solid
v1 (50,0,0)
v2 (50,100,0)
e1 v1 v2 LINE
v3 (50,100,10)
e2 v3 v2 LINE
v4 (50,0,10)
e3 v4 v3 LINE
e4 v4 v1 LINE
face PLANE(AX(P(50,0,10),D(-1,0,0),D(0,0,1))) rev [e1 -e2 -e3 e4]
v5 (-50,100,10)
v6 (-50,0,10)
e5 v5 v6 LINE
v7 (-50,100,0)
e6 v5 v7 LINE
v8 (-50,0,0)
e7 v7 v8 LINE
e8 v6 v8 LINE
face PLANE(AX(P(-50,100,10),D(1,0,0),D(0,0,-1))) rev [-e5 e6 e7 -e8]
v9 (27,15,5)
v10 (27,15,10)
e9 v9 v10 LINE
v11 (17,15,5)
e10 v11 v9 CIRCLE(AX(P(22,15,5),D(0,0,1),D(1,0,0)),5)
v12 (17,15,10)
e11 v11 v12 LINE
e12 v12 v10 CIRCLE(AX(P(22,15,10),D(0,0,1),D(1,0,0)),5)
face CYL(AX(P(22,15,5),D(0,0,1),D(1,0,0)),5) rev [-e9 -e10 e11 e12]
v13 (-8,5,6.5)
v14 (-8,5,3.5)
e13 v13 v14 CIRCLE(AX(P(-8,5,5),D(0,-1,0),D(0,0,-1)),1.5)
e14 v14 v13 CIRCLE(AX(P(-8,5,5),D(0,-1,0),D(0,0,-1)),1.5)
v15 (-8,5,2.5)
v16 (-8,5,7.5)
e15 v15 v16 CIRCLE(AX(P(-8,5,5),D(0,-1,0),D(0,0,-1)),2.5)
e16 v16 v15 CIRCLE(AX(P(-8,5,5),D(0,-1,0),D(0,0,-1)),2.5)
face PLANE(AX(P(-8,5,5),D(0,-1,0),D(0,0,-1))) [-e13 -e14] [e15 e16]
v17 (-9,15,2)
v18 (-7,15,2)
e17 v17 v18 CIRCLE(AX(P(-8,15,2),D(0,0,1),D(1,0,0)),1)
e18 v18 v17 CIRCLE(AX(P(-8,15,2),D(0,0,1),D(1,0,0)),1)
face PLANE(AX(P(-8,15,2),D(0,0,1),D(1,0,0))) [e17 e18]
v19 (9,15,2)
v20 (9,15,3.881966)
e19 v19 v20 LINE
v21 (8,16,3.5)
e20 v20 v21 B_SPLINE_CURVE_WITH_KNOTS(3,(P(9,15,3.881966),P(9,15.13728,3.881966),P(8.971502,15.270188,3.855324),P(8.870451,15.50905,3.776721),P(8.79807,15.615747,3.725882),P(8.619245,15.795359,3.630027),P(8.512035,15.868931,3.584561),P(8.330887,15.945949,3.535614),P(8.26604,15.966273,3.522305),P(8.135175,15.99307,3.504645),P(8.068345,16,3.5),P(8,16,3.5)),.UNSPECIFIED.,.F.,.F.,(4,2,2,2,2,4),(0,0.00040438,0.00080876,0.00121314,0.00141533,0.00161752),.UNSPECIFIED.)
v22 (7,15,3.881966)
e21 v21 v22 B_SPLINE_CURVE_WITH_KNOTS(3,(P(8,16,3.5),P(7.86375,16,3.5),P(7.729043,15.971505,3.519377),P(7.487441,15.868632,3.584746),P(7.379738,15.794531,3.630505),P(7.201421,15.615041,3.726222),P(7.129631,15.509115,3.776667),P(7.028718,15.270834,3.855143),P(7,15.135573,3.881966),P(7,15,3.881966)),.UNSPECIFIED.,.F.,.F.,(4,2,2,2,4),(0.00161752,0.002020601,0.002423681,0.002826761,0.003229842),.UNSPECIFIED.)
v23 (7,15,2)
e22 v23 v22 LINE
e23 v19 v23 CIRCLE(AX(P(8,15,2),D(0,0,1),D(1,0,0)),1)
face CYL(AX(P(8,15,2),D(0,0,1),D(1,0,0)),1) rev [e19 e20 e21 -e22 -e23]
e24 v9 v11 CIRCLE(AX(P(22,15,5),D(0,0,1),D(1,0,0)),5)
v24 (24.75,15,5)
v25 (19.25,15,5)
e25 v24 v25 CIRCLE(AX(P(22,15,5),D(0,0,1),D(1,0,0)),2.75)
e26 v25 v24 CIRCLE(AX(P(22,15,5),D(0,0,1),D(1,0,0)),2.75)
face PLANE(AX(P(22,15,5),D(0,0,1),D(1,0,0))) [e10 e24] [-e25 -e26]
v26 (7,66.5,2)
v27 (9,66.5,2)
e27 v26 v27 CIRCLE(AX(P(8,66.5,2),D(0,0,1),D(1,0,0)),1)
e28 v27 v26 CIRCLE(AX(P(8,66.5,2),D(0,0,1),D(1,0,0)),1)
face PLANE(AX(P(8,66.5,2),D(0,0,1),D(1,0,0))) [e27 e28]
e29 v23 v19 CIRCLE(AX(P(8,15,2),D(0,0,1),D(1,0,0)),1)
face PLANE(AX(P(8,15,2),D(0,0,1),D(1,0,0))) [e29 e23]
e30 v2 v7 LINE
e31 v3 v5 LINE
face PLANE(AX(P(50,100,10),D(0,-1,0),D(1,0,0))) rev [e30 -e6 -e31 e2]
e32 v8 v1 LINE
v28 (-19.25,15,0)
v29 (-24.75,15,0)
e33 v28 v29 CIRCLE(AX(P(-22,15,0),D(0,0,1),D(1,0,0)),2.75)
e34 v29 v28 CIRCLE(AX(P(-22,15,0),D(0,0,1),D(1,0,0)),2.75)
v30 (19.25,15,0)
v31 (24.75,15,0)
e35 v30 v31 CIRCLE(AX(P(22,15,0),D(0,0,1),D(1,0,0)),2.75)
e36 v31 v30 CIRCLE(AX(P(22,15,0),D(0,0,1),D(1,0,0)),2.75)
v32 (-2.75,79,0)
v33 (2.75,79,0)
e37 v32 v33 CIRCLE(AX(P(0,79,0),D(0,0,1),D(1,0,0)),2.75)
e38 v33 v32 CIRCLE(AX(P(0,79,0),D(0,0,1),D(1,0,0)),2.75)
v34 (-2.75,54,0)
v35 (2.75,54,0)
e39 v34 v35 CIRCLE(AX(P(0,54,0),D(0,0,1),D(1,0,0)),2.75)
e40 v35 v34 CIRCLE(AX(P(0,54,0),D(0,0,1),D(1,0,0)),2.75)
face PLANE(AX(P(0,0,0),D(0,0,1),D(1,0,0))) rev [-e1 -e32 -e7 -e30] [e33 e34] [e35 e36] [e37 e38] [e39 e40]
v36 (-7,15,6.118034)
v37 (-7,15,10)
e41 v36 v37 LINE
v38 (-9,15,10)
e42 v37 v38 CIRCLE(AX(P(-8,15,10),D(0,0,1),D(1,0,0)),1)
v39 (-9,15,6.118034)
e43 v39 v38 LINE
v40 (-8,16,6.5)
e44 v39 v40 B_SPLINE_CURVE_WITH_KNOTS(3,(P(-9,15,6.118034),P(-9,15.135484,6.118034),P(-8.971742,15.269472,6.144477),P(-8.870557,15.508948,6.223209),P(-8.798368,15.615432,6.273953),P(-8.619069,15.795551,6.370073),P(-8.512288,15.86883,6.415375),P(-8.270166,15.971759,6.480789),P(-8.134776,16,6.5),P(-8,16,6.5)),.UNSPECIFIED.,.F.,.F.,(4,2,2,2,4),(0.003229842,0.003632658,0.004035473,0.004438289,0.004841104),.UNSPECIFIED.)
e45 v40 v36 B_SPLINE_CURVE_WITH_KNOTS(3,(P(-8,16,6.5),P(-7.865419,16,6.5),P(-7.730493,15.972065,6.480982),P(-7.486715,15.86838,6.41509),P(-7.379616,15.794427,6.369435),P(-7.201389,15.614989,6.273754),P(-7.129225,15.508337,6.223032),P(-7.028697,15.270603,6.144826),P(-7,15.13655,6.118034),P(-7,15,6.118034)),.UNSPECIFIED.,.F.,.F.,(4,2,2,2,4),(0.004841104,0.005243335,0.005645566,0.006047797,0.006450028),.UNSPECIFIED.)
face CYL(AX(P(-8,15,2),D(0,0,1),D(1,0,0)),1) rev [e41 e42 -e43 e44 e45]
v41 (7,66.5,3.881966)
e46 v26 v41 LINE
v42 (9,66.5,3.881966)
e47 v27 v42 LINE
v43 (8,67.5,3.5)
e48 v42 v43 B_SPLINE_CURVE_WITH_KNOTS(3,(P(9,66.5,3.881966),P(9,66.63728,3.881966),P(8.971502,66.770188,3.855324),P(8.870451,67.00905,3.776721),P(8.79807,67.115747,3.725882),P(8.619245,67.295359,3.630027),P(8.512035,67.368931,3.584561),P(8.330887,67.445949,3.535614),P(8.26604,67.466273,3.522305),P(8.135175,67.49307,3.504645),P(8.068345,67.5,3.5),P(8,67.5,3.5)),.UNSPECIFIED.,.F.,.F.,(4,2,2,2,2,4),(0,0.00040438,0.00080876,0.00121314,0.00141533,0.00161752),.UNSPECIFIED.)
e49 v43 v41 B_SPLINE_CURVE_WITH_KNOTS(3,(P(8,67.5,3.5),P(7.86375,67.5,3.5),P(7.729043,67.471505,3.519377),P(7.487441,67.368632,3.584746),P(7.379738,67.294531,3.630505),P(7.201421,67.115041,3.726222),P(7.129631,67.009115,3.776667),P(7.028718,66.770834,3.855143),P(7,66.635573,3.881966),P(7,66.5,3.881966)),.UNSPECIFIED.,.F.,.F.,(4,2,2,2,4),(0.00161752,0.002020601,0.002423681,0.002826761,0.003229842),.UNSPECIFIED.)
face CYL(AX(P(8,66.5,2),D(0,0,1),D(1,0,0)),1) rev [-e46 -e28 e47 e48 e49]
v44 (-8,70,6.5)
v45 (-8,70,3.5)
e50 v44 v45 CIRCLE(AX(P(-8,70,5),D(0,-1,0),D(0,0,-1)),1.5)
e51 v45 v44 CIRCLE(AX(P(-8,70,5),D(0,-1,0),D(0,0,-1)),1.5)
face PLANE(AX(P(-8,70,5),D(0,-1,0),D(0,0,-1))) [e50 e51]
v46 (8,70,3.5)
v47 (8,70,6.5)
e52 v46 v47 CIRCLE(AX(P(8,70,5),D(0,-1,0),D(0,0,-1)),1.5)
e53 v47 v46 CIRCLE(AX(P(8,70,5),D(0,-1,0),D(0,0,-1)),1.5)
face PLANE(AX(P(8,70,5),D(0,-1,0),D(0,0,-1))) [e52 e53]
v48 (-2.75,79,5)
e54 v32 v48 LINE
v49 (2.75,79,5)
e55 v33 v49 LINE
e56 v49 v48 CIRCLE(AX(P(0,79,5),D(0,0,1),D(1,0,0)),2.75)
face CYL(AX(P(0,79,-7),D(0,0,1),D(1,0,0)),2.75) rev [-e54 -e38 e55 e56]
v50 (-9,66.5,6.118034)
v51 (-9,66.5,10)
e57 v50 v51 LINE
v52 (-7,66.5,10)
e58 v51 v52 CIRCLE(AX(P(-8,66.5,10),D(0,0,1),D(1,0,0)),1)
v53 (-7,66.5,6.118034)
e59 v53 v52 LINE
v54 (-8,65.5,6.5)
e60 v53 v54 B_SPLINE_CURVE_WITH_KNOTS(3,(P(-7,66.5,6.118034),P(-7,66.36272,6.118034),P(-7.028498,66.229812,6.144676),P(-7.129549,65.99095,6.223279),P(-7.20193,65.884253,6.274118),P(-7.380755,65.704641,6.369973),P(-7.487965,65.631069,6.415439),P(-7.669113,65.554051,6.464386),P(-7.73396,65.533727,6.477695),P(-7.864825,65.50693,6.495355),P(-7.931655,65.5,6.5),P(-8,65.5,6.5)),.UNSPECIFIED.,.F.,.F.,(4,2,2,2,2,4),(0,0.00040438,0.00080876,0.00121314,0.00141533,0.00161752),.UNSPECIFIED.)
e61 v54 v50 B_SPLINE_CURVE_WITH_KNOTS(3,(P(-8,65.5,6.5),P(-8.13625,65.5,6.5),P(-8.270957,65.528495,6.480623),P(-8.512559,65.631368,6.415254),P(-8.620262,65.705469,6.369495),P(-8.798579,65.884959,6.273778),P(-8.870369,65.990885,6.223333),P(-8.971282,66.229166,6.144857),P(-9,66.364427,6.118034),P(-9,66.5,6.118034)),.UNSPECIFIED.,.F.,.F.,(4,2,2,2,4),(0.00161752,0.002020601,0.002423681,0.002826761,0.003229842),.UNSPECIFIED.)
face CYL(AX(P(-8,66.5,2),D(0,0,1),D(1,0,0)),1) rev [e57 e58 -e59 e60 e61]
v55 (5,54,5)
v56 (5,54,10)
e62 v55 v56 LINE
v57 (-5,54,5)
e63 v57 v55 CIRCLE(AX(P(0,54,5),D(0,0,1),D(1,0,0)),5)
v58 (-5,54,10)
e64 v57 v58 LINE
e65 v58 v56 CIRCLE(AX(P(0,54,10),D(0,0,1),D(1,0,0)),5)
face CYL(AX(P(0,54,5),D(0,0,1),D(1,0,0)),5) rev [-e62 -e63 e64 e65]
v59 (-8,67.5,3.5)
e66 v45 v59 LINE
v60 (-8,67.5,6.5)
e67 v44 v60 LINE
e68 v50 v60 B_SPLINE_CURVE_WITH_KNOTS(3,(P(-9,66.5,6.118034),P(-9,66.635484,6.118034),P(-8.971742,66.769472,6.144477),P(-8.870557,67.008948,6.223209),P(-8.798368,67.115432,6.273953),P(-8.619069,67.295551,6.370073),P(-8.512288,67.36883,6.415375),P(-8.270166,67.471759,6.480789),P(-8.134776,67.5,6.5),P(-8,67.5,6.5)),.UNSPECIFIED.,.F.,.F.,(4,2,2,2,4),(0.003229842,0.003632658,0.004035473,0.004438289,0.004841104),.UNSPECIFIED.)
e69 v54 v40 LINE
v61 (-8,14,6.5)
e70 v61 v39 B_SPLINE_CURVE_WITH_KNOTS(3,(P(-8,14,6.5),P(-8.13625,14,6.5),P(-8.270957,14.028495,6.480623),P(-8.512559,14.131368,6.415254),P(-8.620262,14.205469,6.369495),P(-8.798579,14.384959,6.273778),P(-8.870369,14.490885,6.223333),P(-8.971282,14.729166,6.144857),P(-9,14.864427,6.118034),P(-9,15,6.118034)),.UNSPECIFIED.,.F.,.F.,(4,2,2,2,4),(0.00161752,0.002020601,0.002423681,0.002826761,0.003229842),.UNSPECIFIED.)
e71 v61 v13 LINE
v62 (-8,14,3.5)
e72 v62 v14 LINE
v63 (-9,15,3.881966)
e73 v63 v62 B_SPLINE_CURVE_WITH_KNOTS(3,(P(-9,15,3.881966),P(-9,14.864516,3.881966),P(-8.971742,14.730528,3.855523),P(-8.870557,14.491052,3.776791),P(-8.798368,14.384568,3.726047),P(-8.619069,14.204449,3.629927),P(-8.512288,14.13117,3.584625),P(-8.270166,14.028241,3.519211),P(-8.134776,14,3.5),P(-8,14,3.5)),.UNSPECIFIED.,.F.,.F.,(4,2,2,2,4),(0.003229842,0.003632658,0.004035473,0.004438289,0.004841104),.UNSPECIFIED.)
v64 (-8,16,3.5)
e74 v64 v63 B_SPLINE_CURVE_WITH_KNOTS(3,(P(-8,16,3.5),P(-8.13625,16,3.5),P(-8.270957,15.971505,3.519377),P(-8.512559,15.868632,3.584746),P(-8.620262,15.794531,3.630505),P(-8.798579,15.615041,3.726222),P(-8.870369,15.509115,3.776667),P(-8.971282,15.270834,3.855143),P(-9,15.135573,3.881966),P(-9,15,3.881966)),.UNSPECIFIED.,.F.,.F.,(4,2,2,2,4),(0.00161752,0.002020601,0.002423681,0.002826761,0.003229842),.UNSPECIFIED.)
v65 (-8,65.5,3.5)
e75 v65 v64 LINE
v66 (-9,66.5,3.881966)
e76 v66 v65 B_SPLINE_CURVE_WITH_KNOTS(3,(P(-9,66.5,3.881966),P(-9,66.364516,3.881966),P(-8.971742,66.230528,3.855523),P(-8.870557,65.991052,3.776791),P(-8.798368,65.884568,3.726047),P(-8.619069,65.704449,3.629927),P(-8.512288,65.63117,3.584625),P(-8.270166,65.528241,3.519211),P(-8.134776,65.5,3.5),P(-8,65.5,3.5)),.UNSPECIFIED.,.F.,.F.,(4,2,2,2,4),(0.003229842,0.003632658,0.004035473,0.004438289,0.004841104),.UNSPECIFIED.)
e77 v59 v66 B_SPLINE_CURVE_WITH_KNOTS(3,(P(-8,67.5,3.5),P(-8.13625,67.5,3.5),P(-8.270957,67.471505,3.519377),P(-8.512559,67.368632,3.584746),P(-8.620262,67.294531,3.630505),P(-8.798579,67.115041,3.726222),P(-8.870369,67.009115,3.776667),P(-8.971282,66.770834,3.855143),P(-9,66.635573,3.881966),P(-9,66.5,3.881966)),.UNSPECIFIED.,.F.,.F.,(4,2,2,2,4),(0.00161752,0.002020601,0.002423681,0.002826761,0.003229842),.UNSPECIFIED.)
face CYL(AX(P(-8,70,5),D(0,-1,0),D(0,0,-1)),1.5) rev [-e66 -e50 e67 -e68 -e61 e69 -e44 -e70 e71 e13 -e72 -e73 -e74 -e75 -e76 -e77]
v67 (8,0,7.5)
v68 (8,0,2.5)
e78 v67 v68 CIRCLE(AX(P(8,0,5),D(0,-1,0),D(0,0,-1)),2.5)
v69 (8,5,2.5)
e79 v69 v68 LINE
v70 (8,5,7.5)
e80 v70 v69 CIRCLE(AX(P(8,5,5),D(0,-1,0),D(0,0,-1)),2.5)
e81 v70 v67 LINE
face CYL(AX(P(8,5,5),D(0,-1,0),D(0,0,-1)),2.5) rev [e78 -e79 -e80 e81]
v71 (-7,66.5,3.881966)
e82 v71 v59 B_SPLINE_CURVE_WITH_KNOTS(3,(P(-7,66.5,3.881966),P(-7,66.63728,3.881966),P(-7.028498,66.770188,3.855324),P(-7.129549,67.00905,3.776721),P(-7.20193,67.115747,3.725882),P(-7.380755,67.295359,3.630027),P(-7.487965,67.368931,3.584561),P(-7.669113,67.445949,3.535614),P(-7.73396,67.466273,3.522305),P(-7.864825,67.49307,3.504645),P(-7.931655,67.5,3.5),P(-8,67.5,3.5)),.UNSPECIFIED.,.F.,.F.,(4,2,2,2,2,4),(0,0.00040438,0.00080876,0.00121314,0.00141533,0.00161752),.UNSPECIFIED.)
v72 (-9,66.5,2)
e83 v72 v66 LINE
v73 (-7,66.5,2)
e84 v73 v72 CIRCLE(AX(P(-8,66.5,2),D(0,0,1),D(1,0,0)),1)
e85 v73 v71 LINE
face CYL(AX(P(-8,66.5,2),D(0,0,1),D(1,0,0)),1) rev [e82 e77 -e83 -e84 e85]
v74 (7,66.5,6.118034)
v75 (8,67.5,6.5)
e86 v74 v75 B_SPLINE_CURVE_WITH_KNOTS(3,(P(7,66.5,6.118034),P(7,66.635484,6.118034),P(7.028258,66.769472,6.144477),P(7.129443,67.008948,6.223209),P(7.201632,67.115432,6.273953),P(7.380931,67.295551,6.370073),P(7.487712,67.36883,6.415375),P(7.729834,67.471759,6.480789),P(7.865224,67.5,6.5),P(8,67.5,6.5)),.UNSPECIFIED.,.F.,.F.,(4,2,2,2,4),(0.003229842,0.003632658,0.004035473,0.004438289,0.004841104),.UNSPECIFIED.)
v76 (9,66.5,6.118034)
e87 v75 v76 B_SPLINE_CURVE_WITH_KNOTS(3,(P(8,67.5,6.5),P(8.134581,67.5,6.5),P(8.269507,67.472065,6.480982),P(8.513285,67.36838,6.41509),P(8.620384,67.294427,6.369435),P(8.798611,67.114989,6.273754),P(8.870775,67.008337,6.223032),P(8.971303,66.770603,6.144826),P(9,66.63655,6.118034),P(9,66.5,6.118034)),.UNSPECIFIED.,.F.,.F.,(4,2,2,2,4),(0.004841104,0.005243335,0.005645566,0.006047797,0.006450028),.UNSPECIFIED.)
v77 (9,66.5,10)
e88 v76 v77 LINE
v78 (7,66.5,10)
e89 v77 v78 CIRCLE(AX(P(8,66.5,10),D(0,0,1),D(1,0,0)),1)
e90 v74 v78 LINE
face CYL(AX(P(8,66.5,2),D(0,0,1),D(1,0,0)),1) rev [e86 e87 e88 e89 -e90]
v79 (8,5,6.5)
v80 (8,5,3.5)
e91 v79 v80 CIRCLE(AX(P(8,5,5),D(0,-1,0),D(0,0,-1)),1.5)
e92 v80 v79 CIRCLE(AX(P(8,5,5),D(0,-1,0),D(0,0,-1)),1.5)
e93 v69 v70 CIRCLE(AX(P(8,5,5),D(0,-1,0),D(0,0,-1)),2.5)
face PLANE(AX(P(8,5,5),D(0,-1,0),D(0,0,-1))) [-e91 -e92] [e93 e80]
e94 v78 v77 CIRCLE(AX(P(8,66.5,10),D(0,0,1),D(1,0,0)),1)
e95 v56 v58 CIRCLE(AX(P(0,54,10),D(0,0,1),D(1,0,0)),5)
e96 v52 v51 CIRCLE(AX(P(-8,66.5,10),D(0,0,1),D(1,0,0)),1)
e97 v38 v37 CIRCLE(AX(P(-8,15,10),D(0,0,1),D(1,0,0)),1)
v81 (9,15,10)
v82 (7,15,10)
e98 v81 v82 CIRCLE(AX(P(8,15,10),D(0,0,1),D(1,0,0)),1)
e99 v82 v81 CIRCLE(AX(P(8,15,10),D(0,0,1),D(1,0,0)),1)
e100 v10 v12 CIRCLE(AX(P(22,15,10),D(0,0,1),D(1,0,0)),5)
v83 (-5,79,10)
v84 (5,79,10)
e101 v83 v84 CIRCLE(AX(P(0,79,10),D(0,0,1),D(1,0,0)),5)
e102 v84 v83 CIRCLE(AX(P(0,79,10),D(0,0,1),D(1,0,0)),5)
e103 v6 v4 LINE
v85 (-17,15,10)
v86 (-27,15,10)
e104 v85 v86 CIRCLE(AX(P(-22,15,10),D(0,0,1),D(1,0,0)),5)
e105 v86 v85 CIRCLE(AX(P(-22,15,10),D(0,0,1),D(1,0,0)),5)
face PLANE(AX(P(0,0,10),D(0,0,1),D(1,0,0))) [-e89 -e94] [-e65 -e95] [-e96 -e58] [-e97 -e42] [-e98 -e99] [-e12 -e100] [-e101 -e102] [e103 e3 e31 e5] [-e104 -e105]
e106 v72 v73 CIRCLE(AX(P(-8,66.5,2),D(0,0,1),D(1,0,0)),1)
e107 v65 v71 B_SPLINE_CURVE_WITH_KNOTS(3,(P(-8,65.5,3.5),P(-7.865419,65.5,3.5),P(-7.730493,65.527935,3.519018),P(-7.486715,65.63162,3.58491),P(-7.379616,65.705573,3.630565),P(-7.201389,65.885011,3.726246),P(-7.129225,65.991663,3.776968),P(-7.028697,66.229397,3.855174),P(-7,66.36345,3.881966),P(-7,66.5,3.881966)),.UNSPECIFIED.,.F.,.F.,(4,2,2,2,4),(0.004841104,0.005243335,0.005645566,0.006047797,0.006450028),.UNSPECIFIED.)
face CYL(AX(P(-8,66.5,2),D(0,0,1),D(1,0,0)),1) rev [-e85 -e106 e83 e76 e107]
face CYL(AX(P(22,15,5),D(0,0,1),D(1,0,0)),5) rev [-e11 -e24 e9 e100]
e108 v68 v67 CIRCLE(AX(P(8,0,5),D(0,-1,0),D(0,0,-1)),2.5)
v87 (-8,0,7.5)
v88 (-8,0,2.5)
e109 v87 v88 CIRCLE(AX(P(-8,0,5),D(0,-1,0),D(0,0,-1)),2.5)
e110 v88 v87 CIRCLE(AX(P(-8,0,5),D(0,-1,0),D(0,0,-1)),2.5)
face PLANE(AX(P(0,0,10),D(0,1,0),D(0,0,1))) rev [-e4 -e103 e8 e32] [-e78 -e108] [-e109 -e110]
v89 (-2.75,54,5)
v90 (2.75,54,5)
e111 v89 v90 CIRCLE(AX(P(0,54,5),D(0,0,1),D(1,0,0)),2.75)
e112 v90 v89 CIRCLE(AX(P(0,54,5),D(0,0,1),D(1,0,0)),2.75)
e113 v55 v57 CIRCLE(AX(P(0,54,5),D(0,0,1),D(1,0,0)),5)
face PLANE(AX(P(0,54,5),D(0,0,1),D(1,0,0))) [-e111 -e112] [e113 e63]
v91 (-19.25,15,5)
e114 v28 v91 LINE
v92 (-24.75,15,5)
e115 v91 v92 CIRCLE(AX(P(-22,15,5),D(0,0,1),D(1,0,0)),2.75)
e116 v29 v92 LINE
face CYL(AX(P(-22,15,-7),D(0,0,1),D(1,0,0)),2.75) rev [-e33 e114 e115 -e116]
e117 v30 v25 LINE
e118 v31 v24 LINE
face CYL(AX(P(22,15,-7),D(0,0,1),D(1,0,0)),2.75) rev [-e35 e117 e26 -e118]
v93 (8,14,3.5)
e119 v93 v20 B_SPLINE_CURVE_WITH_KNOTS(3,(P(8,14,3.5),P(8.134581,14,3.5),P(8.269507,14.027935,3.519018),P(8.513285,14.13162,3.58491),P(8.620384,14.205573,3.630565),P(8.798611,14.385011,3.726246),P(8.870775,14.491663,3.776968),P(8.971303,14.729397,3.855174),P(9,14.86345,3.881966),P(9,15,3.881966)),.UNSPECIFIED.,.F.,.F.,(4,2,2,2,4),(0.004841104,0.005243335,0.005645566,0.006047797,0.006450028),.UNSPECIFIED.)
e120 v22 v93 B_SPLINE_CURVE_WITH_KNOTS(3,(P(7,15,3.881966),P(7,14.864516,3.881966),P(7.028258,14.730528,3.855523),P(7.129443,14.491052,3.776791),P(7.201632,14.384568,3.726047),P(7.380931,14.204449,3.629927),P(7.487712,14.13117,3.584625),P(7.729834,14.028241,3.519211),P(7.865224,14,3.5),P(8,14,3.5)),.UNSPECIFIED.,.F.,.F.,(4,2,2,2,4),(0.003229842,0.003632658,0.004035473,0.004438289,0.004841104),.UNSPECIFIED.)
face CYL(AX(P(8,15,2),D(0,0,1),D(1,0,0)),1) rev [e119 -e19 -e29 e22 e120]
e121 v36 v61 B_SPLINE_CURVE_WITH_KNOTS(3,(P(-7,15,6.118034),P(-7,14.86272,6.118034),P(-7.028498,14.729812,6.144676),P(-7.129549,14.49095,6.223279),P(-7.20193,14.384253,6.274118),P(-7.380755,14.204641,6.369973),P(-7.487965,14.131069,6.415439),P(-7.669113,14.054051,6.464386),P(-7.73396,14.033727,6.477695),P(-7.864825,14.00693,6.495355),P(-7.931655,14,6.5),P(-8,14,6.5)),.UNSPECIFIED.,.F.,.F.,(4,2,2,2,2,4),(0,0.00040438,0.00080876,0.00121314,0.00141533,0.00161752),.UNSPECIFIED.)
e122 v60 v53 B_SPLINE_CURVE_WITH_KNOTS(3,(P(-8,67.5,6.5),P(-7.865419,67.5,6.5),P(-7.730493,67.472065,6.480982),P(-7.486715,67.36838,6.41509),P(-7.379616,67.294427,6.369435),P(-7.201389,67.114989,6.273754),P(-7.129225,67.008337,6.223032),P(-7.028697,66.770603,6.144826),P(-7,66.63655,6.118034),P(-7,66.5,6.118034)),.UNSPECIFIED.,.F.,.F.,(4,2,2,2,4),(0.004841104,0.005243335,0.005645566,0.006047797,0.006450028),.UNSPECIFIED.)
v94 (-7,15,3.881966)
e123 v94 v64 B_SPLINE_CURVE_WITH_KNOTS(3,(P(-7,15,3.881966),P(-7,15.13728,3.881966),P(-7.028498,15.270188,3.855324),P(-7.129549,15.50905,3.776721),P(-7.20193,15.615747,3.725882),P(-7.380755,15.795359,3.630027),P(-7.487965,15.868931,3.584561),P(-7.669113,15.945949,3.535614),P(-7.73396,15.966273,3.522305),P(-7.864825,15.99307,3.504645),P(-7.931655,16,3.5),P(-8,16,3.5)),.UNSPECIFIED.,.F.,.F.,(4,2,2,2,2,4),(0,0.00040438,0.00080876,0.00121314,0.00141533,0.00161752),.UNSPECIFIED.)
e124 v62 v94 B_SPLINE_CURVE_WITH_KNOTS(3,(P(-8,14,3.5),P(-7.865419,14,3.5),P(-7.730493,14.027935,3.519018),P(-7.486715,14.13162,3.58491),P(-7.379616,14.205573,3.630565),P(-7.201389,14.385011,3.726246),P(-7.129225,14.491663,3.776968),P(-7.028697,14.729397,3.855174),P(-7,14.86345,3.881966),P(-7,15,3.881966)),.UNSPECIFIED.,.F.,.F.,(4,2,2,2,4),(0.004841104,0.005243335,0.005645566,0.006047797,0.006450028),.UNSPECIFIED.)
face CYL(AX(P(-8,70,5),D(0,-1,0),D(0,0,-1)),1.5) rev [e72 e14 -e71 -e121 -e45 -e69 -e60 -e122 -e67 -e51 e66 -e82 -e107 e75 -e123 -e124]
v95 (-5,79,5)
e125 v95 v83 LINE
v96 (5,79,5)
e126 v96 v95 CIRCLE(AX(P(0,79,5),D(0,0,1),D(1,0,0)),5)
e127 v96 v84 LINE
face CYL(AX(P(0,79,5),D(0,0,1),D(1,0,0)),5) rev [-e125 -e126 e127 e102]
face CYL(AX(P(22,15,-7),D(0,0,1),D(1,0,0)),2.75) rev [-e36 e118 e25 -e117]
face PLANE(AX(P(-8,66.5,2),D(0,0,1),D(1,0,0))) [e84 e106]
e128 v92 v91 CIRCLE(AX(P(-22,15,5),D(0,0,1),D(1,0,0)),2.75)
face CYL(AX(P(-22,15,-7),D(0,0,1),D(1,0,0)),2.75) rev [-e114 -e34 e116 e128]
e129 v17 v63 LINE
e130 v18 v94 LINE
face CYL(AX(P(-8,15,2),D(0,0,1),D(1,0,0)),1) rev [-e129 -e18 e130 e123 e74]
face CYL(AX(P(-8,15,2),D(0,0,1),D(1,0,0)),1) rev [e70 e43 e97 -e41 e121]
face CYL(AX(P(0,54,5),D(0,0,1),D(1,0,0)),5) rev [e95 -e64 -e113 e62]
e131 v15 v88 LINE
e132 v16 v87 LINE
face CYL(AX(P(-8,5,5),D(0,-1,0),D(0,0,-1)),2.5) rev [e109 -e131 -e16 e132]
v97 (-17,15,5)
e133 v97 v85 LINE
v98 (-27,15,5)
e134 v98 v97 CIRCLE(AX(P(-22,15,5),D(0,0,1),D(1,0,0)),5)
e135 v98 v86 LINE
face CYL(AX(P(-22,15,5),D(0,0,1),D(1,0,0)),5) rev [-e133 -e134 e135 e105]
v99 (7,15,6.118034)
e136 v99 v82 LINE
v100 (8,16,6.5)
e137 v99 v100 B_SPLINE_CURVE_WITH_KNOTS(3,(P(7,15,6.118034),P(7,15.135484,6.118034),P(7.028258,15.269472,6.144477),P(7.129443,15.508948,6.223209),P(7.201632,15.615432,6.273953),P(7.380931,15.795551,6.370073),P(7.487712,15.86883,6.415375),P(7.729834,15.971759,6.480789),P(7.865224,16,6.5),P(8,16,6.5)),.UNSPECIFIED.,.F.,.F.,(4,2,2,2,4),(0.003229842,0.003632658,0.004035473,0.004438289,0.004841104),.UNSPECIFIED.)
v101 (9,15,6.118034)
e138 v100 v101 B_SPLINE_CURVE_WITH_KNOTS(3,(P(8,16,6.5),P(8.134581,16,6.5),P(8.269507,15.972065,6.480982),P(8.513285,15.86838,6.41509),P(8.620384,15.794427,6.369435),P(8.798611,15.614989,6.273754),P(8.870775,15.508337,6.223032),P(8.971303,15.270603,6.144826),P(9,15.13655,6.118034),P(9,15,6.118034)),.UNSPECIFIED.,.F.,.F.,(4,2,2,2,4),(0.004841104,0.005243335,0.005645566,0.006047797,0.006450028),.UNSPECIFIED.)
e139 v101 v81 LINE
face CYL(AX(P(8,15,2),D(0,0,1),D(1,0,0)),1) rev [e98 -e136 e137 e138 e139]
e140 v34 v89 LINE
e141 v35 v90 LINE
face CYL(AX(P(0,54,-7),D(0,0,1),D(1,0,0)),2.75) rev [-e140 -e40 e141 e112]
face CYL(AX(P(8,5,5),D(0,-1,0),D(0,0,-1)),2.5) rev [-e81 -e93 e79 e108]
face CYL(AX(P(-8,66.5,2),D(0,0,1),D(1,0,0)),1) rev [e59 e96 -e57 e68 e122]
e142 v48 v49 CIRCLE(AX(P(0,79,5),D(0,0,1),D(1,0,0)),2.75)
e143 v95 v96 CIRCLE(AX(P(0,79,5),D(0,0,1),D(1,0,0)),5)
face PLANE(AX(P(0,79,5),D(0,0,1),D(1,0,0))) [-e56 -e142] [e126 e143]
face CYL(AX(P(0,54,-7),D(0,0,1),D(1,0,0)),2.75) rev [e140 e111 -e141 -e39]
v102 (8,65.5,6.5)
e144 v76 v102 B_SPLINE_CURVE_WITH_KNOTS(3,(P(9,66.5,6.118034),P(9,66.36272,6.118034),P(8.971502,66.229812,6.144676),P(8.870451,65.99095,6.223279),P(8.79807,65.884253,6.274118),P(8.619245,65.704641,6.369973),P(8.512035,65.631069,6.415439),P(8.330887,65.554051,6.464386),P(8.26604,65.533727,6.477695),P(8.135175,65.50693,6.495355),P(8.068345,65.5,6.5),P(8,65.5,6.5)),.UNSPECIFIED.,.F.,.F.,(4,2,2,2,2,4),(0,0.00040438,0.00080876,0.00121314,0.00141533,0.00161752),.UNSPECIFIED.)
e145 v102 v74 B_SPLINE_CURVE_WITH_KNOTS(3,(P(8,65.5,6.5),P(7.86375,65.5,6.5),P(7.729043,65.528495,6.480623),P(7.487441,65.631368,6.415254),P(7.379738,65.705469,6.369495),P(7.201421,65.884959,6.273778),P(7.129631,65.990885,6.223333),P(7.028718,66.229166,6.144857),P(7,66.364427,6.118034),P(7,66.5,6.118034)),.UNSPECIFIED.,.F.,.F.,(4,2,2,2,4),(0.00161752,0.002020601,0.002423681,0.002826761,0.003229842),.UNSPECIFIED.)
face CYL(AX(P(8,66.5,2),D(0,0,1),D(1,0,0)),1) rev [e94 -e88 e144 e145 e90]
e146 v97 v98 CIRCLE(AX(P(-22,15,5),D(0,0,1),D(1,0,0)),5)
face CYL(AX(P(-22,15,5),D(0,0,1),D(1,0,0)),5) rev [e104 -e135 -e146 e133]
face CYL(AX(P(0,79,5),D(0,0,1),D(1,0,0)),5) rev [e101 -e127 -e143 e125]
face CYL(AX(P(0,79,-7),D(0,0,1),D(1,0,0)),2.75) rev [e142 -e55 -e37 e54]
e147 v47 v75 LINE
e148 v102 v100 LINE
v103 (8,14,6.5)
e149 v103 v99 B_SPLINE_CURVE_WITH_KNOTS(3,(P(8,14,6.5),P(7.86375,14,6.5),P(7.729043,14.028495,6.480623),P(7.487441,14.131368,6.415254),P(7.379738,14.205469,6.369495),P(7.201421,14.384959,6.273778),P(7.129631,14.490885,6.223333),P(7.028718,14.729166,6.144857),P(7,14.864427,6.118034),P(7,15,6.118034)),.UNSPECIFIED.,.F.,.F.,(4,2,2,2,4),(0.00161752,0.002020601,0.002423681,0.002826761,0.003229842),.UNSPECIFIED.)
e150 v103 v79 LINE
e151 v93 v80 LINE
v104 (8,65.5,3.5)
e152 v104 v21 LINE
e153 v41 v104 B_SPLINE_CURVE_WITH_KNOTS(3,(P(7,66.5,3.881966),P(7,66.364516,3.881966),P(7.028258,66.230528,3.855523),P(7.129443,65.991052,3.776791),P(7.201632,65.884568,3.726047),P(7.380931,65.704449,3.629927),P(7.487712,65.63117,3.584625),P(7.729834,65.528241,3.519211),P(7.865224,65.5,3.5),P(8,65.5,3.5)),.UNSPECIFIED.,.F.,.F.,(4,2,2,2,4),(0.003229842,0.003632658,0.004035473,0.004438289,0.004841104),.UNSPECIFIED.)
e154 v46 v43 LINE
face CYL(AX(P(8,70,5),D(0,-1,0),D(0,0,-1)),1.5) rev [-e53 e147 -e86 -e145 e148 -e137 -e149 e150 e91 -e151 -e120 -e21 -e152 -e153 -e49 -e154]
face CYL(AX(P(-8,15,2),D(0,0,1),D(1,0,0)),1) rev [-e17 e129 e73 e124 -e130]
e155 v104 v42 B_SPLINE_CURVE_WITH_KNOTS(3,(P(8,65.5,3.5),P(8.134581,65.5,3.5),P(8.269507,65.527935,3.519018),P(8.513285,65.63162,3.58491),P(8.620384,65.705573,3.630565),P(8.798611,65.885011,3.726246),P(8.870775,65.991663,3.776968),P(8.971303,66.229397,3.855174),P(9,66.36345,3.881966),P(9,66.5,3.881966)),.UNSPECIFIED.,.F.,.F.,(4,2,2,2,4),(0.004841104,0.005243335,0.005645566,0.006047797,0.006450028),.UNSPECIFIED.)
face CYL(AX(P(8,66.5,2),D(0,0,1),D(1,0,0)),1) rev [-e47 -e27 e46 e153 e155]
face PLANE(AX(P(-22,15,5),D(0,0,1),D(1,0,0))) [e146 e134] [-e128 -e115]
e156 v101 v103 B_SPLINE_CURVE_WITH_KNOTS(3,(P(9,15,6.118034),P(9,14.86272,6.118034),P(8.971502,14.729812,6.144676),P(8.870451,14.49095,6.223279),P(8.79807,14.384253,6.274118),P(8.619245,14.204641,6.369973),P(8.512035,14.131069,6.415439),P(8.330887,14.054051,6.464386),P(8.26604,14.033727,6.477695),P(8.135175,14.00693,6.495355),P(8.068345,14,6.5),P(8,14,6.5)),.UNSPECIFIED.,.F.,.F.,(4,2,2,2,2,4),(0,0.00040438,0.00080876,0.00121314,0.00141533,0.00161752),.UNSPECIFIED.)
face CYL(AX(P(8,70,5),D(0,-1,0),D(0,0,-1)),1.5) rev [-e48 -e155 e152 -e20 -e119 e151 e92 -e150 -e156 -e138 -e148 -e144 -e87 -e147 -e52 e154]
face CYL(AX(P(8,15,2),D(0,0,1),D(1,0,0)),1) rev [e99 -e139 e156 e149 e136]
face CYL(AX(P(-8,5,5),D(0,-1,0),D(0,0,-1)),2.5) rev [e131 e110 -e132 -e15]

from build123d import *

# Parameters (mm, degrees)
BASE_PLATE_100X100X10_DEPTH  = 10
COUNTERBORE_SKETCH_R         = 5
COUNTERBORES_4X_10X5_DEPTH   = 5
CLEARANCE_HOLE_SKETCH_R      = 2.75
CLEARANCE_HOLES_4X_5_5_DEPTH = 12
SMALL_HOLE_SKETCH_R          = 1
SMALL_HOLES_4X_2X8_DEPTH     = 8
RECESS_SKETCH_R              = 2.5
RECESSES_2X_5X5_DEPTH        = 5
STEPPED_HOLE_SKETCH_R        = 1.5
STEPPED_HOLES_2X_3_DEPTH     = 70


with BuildPart() as part:
    # Base Plate Sketch → Base Plate 100x100x10 (new body)
    with BuildSketch(Plane.XY):
        Polygon((0, 0), (50, 0), (50, 100), (-50, 100), (-50, 0), align=None)
    extrude(amount=BASE_PLATE_100X100X10_DEPTH)

    # Counterbore Sketch → Counterbores 4x_10x5 (cut)
    with BuildSketch(Plane.XY.offset(10)):
        with Locations((0, 54)):
            Circle(COUNTERBORE_SKETCH_R)
        with Locations((0, 79)):
            Circle(COUNTERBORE_SKETCH_R)
        with Locations((22, 15)):
            Circle(COUNTERBORE_SKETCH_R)
        with Locations((-22, 15)):
            Circle(COUNTERBORE_SKETCH_R)
    extrude(amount=-COUNTERBORES_4X_10X5_DEPTH, mode=Mode.SUBTRACT)

    # Clearance Hole Sketch → Clearance Holes 4x_5.5 (cut)
    with BuildSketch(Plane.XY.offset(5)):
        with Locations((0, 79)):
            Circle(CLEARANCE_HOLE_SKETCH_R)
        with Locations((0, 54)):
            Circle(CLEARANCE_HOLE_SKETCH_R)
        with Locations((22, 15)):
            Circle(CLEARANCE_HOLE_SKETCH_R)
        with Locations((-22, 15)):
            Circle(CLEARANCE_HOLE_SKETCH_R)
    extrude(amount=-CLEARANCE_HOLES_4X_5_5_DEPTH, mode=Mode.SUBTRACT)

    # Small Hole Sketch → Small Holes 4x_2x8 (cut)
    with BuildSketch(Plane.XY.offset(10)):
        with Locations((8, 15)):
            Circle(SMALL_HOLE_SKETCH_R)
        with Locations((-8, 15)):
            Circle(SMALL_HOLE_SKETCH_R)
        with Locations((8, 66.5)):
            Circle(SMALL_HOLE_SKETCH_R)
        with Locations((-8, 66.5)):
            Circle(SMALL_HOLE_SKETCH_R)
    extrude(amount=-SMALL_HOLES_4X_2X8_DEPTH, mode=Mode.SUBTRACT)

    # Recess Sketch → Recesses 2x_5x5 (cut)
    with BuildSketch(Plane.XZ):
        with Locations(Location((-8, 5, 0), (0, 0, 270))):
            Circle(RECESS_SKETCH_R)
        with Locations(Location((8, 5, 0), (0, 0, 270))):
            Circle(RECESS_SKETCH_R)
    extrude(amount=-RECESSES_2X_5X5_DEPTH, mode=Mode.SUBTRACT)

    # Stepped Hole Sketch → Stepped Holes 2x_3 (cut)
    with BuildSketch(Plane.XZ):
        with Locations(Location((8, 5, 0), (0, 0, 270))):
            Circle(STEPPED_HOLE_SKETCH_R)
        with Locations(Location((-8, 5, 0), (0, 0, 270))):
            Circle(STEPPED_HOLE_SKETCH_R)
    extrude(amount=-STEPPED_HOLES_2X_3_DEPTH, mode=Mode.SUBTRACT)


solid = part.part
